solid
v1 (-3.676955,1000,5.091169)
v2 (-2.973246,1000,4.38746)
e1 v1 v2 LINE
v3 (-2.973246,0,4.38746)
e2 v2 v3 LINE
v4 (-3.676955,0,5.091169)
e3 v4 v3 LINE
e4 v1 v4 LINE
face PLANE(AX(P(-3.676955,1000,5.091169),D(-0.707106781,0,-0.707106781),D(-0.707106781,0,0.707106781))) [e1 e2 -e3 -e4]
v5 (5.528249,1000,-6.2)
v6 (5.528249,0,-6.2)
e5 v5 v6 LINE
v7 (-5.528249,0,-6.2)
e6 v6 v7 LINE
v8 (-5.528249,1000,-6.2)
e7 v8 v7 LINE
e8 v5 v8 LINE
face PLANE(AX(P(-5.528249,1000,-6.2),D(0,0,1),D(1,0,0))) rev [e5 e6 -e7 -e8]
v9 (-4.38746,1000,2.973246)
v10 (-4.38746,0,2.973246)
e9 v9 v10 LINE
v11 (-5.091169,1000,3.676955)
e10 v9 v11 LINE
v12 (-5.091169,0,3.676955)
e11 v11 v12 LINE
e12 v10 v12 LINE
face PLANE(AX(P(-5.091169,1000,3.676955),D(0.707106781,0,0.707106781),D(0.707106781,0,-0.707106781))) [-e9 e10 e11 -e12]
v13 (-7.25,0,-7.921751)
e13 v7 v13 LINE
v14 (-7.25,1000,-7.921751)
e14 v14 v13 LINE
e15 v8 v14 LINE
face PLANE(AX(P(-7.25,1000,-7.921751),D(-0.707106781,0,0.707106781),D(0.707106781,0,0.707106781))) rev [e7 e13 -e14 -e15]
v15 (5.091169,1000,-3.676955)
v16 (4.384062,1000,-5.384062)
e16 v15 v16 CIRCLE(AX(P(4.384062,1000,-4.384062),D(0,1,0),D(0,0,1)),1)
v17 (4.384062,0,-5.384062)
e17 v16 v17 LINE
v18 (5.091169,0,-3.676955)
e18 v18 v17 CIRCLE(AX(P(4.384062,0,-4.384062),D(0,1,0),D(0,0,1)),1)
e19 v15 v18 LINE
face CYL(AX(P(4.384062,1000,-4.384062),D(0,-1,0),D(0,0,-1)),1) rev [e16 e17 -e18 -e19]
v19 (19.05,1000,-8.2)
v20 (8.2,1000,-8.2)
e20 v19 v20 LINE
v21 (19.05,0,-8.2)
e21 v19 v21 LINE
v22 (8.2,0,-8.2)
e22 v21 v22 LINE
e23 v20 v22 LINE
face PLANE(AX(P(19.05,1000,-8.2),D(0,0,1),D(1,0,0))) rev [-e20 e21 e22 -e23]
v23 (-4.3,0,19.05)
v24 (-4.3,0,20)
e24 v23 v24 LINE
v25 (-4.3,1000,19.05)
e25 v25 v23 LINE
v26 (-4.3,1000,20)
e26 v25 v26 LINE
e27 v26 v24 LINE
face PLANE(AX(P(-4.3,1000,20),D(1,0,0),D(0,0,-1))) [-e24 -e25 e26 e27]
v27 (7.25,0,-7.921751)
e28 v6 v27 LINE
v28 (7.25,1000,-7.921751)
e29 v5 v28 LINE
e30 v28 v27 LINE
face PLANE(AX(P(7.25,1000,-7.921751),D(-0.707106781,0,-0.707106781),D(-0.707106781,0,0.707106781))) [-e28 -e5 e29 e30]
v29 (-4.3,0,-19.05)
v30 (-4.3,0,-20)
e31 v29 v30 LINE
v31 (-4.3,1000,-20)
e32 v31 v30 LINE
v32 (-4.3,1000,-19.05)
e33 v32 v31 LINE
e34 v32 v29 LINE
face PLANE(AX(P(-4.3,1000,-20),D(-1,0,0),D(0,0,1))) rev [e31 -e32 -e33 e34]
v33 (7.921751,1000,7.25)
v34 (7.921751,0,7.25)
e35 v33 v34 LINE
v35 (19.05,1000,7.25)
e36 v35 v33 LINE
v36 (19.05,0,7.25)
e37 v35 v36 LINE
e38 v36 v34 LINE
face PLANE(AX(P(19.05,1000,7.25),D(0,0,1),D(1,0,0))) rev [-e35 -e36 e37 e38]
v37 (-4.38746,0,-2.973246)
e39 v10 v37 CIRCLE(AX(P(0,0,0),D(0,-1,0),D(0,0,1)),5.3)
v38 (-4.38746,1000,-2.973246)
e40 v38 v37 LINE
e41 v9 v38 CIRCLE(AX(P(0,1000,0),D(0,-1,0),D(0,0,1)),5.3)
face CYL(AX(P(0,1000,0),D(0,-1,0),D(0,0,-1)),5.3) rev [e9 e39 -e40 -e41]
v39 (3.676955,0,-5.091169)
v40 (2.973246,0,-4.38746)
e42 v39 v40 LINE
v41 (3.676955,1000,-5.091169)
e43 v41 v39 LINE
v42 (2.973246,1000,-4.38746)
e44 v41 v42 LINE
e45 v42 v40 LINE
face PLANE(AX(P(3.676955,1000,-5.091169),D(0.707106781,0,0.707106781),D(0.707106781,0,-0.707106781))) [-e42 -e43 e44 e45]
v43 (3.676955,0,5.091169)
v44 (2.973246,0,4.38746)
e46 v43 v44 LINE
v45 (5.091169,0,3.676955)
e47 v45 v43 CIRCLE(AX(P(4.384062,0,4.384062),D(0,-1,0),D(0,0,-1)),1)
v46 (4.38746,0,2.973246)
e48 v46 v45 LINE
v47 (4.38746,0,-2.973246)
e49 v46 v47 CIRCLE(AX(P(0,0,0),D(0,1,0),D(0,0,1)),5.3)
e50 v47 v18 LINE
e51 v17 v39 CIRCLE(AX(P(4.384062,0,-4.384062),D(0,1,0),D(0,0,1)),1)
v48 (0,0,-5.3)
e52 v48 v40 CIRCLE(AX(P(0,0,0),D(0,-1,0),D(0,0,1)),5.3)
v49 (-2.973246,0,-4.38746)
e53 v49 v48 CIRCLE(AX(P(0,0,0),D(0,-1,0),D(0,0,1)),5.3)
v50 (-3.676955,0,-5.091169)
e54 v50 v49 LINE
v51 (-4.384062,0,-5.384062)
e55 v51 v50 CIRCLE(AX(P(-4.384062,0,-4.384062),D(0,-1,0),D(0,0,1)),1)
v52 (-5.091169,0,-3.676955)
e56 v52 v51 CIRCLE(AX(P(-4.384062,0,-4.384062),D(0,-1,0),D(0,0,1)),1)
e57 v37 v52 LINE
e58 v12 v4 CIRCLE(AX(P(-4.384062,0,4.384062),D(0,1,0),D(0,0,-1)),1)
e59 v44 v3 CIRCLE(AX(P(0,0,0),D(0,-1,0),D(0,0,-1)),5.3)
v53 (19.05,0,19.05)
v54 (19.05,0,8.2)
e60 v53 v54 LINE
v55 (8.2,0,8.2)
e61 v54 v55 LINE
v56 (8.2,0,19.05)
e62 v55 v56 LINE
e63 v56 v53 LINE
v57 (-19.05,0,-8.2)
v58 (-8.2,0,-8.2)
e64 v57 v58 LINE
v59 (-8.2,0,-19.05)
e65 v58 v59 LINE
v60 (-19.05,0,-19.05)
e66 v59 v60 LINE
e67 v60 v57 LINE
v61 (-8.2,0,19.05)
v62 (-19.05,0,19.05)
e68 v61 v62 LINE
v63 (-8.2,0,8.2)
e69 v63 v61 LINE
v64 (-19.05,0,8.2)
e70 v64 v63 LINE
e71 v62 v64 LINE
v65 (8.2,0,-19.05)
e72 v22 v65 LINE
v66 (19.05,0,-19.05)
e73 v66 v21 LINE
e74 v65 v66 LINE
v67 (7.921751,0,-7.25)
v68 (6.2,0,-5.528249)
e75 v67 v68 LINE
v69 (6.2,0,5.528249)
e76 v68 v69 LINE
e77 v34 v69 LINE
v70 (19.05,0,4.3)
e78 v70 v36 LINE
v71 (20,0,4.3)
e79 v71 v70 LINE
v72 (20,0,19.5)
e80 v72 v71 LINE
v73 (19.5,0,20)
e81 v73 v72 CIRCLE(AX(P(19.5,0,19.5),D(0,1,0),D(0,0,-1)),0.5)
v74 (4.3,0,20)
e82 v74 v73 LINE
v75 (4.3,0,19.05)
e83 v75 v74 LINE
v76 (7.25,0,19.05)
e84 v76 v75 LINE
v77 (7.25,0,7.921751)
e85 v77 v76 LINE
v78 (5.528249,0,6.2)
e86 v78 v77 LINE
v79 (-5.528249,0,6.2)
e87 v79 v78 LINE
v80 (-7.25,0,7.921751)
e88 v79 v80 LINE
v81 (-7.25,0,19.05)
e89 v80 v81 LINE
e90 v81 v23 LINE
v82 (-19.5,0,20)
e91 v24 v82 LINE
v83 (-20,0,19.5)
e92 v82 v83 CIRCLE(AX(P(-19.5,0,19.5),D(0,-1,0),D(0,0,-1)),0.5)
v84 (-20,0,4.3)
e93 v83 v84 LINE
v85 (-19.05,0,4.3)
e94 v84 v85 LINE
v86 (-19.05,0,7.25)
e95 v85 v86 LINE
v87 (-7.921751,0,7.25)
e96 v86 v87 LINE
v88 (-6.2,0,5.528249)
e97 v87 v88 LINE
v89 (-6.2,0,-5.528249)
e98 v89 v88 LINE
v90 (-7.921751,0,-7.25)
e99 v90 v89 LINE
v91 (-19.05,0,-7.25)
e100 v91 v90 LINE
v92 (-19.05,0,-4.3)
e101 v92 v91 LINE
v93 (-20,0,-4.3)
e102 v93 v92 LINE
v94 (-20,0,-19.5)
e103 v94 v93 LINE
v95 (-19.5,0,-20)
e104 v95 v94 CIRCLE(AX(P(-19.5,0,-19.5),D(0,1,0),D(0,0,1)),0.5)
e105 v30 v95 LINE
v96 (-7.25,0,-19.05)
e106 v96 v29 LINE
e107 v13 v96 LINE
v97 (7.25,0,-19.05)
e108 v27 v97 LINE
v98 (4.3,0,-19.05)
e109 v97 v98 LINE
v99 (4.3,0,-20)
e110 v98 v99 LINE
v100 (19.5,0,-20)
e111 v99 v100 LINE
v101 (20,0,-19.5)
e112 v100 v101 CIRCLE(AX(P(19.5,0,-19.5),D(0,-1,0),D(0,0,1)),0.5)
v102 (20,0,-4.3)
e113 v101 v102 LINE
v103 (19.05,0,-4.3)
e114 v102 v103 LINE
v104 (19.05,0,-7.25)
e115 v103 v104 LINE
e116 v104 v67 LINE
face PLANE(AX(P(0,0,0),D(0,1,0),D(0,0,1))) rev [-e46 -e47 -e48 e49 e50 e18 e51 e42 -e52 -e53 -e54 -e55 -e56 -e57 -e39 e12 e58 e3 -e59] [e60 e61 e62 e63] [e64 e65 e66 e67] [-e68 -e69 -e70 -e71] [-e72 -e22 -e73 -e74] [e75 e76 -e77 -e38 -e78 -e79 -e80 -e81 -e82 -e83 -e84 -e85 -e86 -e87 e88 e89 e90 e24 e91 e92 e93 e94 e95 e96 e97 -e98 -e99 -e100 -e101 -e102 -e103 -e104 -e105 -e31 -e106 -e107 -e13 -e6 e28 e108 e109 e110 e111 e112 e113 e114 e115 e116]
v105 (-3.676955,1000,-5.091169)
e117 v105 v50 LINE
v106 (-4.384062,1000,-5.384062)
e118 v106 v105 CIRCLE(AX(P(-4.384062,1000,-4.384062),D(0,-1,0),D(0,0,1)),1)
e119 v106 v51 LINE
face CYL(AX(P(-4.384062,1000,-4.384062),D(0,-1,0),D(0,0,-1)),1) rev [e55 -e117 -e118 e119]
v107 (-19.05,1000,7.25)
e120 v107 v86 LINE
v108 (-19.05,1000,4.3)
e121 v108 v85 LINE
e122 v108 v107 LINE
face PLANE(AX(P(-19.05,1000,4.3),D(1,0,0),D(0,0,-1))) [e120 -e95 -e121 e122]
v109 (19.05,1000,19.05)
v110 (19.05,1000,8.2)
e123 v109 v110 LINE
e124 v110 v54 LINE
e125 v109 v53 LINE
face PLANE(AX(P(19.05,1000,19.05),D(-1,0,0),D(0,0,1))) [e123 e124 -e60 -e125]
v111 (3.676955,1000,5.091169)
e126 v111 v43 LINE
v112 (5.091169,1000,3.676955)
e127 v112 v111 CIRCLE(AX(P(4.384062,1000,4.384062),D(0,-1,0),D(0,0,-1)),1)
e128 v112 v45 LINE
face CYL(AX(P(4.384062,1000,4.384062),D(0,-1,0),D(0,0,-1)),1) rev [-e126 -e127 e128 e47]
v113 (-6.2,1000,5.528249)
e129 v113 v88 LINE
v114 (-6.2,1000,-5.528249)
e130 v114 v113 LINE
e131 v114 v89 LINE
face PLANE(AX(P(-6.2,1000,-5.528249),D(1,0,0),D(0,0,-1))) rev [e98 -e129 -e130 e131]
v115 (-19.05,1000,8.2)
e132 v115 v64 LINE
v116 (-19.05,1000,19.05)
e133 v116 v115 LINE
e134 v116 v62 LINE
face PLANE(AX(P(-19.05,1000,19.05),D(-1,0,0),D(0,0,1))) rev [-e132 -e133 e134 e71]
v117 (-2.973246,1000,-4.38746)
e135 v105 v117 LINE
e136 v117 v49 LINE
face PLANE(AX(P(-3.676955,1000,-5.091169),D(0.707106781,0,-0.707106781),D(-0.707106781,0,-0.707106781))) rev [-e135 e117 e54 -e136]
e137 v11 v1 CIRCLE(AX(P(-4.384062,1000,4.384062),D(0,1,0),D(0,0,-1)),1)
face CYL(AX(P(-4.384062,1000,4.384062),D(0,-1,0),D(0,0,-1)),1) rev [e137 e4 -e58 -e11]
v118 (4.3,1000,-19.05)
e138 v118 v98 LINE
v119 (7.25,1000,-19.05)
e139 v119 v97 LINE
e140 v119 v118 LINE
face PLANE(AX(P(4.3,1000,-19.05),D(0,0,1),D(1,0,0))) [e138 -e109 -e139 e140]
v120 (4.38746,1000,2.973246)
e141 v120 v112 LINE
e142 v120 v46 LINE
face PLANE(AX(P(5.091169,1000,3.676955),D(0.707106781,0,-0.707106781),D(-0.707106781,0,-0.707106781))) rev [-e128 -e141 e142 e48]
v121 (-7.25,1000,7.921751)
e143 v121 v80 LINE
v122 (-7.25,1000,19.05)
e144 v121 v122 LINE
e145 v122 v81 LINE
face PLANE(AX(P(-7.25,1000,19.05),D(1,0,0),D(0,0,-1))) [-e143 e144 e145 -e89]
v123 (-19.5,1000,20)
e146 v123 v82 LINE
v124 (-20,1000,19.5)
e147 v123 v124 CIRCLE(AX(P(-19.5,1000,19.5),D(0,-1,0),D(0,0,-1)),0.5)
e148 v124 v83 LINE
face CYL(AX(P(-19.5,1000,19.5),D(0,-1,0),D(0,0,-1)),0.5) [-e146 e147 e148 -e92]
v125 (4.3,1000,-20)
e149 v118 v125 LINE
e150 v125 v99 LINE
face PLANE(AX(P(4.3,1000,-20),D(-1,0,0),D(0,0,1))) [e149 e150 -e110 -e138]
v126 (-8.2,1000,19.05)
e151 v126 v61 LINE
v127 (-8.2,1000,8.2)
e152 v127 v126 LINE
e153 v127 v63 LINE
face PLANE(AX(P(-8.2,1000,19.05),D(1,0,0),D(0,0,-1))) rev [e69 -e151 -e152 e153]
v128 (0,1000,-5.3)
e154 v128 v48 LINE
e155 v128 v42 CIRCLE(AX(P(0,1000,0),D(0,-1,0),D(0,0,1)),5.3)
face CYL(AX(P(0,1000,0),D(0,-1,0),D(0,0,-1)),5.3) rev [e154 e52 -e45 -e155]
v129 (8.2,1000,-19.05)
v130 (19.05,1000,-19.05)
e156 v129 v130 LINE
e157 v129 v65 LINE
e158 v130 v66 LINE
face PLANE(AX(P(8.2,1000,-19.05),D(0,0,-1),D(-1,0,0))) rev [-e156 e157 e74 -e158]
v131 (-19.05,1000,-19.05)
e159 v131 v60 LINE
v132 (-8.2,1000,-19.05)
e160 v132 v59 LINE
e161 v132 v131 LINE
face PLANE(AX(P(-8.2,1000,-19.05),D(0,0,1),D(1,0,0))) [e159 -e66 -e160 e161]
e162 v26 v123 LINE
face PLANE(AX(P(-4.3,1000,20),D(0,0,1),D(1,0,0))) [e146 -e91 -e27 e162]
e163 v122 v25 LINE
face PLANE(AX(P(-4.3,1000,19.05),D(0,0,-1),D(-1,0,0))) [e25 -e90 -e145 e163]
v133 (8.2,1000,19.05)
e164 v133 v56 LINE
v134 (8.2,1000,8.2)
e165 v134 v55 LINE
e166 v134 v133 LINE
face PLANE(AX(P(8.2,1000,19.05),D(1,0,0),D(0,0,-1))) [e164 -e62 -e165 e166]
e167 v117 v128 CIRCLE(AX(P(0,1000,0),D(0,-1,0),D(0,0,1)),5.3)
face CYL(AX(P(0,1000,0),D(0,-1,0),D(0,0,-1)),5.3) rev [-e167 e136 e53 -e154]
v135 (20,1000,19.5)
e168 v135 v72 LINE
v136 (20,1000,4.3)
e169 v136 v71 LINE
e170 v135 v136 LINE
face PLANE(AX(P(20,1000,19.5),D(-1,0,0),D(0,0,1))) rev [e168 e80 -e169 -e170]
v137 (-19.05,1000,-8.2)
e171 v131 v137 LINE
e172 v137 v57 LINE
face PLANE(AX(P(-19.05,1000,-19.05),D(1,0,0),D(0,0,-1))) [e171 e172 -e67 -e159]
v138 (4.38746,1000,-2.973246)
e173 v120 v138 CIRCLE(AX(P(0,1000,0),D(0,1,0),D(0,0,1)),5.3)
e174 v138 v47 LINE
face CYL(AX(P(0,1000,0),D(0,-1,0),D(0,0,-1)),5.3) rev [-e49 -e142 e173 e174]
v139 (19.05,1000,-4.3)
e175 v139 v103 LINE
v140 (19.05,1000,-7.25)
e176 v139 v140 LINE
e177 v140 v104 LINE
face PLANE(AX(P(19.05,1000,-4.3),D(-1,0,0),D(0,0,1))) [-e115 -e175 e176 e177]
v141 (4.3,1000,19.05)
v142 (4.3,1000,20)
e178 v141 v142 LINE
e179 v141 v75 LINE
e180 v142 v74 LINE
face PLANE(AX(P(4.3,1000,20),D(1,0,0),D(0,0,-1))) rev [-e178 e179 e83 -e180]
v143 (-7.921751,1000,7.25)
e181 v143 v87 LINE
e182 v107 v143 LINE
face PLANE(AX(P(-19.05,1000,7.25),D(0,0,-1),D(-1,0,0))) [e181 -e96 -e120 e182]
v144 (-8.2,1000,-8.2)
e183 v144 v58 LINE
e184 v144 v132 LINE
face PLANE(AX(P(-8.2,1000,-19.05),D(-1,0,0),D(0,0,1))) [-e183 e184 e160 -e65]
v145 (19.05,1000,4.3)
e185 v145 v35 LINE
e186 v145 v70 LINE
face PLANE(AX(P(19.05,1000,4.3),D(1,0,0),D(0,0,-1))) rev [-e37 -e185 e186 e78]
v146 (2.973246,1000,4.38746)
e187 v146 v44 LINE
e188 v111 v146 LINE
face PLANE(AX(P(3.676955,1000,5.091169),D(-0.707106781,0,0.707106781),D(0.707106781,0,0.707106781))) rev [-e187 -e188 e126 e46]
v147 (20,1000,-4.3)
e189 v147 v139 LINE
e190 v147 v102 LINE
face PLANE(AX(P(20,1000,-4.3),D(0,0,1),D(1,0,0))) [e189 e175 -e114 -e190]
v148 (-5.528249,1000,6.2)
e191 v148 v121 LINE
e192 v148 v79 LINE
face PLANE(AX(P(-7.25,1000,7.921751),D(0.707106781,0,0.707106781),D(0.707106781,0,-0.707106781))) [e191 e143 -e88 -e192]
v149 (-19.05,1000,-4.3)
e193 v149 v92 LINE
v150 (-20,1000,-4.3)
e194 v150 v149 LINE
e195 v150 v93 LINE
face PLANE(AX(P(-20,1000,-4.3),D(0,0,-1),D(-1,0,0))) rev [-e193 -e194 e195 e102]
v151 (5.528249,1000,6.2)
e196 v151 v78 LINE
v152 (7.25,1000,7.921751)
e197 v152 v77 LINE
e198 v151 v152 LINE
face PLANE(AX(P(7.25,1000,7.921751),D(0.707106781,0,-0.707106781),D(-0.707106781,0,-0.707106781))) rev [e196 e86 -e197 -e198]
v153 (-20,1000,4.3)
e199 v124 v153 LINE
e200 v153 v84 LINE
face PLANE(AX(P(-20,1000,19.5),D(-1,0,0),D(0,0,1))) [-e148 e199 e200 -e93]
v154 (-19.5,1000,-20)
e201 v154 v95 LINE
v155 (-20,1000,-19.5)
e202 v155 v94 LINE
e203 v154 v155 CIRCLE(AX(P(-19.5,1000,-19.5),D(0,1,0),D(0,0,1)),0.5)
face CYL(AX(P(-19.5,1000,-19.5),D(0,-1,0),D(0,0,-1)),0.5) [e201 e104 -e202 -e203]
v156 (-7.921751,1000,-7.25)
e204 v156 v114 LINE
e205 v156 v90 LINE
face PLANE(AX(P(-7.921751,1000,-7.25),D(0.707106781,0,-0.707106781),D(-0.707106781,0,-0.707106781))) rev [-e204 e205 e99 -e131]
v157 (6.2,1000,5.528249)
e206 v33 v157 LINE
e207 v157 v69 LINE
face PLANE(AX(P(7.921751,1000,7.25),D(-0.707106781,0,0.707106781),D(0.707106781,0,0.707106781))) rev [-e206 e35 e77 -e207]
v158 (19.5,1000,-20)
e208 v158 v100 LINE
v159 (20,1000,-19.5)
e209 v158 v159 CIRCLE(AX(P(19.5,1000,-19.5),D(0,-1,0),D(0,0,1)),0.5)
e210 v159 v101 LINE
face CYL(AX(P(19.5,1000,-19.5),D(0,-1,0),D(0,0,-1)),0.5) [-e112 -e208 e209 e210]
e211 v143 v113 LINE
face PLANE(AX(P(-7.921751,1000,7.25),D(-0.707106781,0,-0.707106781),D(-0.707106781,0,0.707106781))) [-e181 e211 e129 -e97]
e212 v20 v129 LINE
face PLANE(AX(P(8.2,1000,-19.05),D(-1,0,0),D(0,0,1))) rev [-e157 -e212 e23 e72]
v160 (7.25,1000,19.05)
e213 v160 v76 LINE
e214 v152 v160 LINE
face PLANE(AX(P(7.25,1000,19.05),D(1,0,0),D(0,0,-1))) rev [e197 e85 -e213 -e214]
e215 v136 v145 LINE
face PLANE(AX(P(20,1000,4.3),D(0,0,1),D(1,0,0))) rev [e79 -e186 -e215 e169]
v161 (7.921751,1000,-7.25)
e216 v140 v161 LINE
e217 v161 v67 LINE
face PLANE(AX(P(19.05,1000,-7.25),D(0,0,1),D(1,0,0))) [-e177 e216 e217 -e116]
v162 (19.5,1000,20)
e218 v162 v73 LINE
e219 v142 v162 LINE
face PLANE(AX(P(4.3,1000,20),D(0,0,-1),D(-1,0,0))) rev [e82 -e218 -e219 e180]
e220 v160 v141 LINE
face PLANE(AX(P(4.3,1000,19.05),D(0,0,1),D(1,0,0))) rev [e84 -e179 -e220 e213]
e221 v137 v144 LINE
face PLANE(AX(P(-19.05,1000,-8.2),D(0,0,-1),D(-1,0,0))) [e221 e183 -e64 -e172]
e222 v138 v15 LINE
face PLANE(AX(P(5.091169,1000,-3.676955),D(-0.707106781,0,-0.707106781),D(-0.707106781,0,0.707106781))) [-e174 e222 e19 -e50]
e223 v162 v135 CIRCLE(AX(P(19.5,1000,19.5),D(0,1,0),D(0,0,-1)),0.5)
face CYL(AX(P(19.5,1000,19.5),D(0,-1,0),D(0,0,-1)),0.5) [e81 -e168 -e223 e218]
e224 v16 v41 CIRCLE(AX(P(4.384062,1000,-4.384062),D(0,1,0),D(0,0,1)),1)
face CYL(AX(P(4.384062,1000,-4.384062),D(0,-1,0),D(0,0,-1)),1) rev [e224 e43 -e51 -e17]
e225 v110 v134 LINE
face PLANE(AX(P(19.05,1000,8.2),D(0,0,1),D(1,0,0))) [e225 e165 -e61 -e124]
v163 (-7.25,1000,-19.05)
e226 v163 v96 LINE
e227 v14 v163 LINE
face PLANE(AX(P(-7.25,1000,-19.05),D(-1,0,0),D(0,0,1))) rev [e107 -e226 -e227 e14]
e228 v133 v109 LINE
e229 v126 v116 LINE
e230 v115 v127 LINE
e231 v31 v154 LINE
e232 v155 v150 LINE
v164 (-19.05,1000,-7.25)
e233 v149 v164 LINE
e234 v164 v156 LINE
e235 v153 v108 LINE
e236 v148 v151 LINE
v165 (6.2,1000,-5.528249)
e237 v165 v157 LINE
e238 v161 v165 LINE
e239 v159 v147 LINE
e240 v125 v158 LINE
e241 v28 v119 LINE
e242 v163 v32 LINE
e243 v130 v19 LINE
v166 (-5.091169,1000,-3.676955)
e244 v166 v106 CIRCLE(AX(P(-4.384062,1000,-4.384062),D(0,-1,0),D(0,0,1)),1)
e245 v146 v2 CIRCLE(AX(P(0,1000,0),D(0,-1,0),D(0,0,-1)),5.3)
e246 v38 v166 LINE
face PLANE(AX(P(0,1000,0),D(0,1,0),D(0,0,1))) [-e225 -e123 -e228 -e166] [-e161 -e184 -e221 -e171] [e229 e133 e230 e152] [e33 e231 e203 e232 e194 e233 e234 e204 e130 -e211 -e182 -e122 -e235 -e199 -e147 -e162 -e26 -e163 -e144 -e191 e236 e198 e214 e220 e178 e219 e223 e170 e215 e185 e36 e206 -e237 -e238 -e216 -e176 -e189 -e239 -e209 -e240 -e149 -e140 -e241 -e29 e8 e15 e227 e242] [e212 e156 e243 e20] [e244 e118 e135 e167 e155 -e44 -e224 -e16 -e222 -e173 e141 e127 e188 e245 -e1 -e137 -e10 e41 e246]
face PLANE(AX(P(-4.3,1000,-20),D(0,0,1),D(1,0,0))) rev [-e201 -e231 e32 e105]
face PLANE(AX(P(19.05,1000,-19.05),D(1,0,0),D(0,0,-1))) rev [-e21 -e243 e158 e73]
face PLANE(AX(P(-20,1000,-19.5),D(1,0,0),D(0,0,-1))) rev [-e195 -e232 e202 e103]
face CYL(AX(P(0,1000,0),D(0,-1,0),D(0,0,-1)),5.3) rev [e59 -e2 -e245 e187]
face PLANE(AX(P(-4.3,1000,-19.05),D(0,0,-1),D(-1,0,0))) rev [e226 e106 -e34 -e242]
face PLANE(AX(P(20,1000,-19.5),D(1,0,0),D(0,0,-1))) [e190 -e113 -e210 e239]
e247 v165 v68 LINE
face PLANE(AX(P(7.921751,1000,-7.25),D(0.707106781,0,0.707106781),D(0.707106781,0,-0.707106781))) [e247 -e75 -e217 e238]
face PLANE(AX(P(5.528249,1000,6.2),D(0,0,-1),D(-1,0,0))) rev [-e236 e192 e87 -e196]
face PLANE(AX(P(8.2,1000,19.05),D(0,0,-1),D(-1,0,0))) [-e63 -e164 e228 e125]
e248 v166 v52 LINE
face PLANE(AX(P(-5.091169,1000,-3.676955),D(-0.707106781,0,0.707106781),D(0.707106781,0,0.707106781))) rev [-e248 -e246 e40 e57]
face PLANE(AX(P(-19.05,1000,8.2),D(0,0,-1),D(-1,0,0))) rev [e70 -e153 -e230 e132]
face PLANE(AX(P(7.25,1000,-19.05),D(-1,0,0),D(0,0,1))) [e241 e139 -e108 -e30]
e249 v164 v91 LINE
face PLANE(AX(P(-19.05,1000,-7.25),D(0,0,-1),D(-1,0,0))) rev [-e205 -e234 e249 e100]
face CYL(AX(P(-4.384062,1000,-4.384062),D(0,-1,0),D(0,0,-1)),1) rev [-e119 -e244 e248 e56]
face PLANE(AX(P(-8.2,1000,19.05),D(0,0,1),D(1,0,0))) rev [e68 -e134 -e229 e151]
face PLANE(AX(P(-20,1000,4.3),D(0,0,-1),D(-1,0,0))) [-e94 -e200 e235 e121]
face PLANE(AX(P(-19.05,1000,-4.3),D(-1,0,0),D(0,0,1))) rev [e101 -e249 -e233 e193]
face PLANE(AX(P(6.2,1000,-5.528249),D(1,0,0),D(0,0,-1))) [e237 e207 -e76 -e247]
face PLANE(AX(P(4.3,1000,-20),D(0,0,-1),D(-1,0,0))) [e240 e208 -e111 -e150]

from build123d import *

# Parameters (mm, degrees)
SKETCH1_W               = 10.85
SKETCH1_H               = 10.85
BOSS_EXTRUDE1_DEPTH     = 1000
MIRROR2_COPY_1_SKETCH_W = 10.85
MIRROR2_COPY_1_SKETCH_H = 10.85
MIRROR2_COPY_1_DEPTH    = 1000


with BuildPart() as part:
    # Sketch1 → Boss-Extrude1 (new body)
    with BuildSketch(Plane(origin=(0, 0, 0), x_dir=(1, 0, 0), z_dir=(0, 1, 0))):
        with BuildLine():
            Line((-4.3, 20), (-19.5, 20))
            ThreePointArc((-19.5, 20), (-19.853553391, 19.853553391), (-20, 19.5))
            Line((-20, 19.5), (-20, 4.3))
            Line((-20, 4.3), (-19.05, 4.3))
            Line((-19.05, 4.3), (-19.05, 7.25))
            Line((-19.05, 7.25), (-7.921751442, 7.25))
            Line((-7.921751442, 7.25), (-6.2, 5.528248558))
            Line((-6.2, 5.528248558), (-6.2, 0))
            Line((-6.2, 0), (-5.3, 0))
            ThreePointArc((-5.3, 0), (-5.066731596, 1.555066215), (-4.387460025, 2.973246463))
            Line((-4.387460025, 2.973246463), (-5.091168825, 3.676955262))
            ThreePointArc((-5.091168825, 3.676955262), (-5.091168825, 5.091168825), (-3.676955262, 5.091168825))
            Line((-3.676955262, 5.091168825), (-2.973246463, 4.387460025))
            ThreePointArc((-2.973246463, 4.387460025), (-1.555066215, 5.066731596), (0, 5.3))
            Line((0, 5.3), (0, 6.2))
            Line((0, 6.2), (-5.528248558, 6.2))
            Line((-5.528248558, 6.2), (-7.25, 7.921751442))
            Line((-7.25, 7.921751442), (-7.25, 19.05))
            Line((-7.25, 19.05), (-4.3, 19.05))
            Line((-4.3, 19.05), (-4.3, 20))
        make_face()
        with Locations((-13.625, 13.625)):
            Rectangle(SKETCH1_W, SKETCH1_H, mode=Mode.SUBTRACT)
    boss_extrude1 = extrude(amount=BOSS_EXTRUDE1_DEPTH)

    # Mirror1: Boss-Extrude1 across plane
    add(boss_extrude1.mirror(Plane(origin=(0, 0, 0), x_dir=(0, 0, 1), z_dir=(1, 0, 0))))

    # Mirror2: Boss-Extrude1 across plane
    add(boss_extrude1.mirror(Plane.XY))

    # Mirror2 copy 1 sketch → Mirror2 copy 1 (add)
    with BuildSketch(Plane(origin=(0, 0, 0), x_dir=(-1, 0, 0), z_dir=(0, 1, 0))):
        with BuildLine():
            Line((-4.3, 20), (-19.5, 20))
            ThreePointArc((-19.5, 20), (-19.853553391, 19.853553391), (-20, 19.5))
            Line((-20, 19.5), (-20, 4.3))
            Line((-20, 4.3), (-19.05, 4.3))
            Line((-19.05, 4.3), (-19.05, 7.25))
            Line((-19.05, 7.25), (-7.921751442, 7.25))
            Line((-7.921751442, 7.25), (-6.2, 5.528248558))
            Line((-6.2, 5.528248558), (-6.2, 0))
            Line((-6.2, 0), (-5.3, 0))
            ThreePointArc((-5.3, 0), (-5.066731596, 1.555066215), (-4.387460025, 2.973246463))
            Line((-4.387460025, 2.973246463), (-5.091168825, 3.676955262))
            ThreePointArc((-5.091168825, 3.676955262), (-5.091168825, 5.091168825), (-3.676955262, 5.091168825))
            Line((-3.676955262, 5.091168825), (-2.973246463, 4.387460025))
            ThreePointArc((-2.973246463, 4.387460025), (-1.555066215, 5.066731596), (0, 5.3))
            Line((0, 5.3), (0, 6.2))
            Line((0, 6.2), (-5.528248558, 6.2))
            Line((-5.528248558, 6.2), (-7.25, 7.921751442))
            Line((-7.25, 7.921751442), (-7.25, 19.05))
            Line((-7.25, 19.05), (-4.3, 19.05))
            Line((-4.3, 19.05), (-4.3, 20))
        make_face()
        with Locations((-13.625, 13.625)):
            Rectangle(MIRROR2_COPY_1_SKETCH_W, MIRROR2_COPY_1_SKETCH_H, mode=Mode.SUBTRACT)
    extrude(amount=MIRROR2_COPY_1_DEPTH)


solid = part.part
